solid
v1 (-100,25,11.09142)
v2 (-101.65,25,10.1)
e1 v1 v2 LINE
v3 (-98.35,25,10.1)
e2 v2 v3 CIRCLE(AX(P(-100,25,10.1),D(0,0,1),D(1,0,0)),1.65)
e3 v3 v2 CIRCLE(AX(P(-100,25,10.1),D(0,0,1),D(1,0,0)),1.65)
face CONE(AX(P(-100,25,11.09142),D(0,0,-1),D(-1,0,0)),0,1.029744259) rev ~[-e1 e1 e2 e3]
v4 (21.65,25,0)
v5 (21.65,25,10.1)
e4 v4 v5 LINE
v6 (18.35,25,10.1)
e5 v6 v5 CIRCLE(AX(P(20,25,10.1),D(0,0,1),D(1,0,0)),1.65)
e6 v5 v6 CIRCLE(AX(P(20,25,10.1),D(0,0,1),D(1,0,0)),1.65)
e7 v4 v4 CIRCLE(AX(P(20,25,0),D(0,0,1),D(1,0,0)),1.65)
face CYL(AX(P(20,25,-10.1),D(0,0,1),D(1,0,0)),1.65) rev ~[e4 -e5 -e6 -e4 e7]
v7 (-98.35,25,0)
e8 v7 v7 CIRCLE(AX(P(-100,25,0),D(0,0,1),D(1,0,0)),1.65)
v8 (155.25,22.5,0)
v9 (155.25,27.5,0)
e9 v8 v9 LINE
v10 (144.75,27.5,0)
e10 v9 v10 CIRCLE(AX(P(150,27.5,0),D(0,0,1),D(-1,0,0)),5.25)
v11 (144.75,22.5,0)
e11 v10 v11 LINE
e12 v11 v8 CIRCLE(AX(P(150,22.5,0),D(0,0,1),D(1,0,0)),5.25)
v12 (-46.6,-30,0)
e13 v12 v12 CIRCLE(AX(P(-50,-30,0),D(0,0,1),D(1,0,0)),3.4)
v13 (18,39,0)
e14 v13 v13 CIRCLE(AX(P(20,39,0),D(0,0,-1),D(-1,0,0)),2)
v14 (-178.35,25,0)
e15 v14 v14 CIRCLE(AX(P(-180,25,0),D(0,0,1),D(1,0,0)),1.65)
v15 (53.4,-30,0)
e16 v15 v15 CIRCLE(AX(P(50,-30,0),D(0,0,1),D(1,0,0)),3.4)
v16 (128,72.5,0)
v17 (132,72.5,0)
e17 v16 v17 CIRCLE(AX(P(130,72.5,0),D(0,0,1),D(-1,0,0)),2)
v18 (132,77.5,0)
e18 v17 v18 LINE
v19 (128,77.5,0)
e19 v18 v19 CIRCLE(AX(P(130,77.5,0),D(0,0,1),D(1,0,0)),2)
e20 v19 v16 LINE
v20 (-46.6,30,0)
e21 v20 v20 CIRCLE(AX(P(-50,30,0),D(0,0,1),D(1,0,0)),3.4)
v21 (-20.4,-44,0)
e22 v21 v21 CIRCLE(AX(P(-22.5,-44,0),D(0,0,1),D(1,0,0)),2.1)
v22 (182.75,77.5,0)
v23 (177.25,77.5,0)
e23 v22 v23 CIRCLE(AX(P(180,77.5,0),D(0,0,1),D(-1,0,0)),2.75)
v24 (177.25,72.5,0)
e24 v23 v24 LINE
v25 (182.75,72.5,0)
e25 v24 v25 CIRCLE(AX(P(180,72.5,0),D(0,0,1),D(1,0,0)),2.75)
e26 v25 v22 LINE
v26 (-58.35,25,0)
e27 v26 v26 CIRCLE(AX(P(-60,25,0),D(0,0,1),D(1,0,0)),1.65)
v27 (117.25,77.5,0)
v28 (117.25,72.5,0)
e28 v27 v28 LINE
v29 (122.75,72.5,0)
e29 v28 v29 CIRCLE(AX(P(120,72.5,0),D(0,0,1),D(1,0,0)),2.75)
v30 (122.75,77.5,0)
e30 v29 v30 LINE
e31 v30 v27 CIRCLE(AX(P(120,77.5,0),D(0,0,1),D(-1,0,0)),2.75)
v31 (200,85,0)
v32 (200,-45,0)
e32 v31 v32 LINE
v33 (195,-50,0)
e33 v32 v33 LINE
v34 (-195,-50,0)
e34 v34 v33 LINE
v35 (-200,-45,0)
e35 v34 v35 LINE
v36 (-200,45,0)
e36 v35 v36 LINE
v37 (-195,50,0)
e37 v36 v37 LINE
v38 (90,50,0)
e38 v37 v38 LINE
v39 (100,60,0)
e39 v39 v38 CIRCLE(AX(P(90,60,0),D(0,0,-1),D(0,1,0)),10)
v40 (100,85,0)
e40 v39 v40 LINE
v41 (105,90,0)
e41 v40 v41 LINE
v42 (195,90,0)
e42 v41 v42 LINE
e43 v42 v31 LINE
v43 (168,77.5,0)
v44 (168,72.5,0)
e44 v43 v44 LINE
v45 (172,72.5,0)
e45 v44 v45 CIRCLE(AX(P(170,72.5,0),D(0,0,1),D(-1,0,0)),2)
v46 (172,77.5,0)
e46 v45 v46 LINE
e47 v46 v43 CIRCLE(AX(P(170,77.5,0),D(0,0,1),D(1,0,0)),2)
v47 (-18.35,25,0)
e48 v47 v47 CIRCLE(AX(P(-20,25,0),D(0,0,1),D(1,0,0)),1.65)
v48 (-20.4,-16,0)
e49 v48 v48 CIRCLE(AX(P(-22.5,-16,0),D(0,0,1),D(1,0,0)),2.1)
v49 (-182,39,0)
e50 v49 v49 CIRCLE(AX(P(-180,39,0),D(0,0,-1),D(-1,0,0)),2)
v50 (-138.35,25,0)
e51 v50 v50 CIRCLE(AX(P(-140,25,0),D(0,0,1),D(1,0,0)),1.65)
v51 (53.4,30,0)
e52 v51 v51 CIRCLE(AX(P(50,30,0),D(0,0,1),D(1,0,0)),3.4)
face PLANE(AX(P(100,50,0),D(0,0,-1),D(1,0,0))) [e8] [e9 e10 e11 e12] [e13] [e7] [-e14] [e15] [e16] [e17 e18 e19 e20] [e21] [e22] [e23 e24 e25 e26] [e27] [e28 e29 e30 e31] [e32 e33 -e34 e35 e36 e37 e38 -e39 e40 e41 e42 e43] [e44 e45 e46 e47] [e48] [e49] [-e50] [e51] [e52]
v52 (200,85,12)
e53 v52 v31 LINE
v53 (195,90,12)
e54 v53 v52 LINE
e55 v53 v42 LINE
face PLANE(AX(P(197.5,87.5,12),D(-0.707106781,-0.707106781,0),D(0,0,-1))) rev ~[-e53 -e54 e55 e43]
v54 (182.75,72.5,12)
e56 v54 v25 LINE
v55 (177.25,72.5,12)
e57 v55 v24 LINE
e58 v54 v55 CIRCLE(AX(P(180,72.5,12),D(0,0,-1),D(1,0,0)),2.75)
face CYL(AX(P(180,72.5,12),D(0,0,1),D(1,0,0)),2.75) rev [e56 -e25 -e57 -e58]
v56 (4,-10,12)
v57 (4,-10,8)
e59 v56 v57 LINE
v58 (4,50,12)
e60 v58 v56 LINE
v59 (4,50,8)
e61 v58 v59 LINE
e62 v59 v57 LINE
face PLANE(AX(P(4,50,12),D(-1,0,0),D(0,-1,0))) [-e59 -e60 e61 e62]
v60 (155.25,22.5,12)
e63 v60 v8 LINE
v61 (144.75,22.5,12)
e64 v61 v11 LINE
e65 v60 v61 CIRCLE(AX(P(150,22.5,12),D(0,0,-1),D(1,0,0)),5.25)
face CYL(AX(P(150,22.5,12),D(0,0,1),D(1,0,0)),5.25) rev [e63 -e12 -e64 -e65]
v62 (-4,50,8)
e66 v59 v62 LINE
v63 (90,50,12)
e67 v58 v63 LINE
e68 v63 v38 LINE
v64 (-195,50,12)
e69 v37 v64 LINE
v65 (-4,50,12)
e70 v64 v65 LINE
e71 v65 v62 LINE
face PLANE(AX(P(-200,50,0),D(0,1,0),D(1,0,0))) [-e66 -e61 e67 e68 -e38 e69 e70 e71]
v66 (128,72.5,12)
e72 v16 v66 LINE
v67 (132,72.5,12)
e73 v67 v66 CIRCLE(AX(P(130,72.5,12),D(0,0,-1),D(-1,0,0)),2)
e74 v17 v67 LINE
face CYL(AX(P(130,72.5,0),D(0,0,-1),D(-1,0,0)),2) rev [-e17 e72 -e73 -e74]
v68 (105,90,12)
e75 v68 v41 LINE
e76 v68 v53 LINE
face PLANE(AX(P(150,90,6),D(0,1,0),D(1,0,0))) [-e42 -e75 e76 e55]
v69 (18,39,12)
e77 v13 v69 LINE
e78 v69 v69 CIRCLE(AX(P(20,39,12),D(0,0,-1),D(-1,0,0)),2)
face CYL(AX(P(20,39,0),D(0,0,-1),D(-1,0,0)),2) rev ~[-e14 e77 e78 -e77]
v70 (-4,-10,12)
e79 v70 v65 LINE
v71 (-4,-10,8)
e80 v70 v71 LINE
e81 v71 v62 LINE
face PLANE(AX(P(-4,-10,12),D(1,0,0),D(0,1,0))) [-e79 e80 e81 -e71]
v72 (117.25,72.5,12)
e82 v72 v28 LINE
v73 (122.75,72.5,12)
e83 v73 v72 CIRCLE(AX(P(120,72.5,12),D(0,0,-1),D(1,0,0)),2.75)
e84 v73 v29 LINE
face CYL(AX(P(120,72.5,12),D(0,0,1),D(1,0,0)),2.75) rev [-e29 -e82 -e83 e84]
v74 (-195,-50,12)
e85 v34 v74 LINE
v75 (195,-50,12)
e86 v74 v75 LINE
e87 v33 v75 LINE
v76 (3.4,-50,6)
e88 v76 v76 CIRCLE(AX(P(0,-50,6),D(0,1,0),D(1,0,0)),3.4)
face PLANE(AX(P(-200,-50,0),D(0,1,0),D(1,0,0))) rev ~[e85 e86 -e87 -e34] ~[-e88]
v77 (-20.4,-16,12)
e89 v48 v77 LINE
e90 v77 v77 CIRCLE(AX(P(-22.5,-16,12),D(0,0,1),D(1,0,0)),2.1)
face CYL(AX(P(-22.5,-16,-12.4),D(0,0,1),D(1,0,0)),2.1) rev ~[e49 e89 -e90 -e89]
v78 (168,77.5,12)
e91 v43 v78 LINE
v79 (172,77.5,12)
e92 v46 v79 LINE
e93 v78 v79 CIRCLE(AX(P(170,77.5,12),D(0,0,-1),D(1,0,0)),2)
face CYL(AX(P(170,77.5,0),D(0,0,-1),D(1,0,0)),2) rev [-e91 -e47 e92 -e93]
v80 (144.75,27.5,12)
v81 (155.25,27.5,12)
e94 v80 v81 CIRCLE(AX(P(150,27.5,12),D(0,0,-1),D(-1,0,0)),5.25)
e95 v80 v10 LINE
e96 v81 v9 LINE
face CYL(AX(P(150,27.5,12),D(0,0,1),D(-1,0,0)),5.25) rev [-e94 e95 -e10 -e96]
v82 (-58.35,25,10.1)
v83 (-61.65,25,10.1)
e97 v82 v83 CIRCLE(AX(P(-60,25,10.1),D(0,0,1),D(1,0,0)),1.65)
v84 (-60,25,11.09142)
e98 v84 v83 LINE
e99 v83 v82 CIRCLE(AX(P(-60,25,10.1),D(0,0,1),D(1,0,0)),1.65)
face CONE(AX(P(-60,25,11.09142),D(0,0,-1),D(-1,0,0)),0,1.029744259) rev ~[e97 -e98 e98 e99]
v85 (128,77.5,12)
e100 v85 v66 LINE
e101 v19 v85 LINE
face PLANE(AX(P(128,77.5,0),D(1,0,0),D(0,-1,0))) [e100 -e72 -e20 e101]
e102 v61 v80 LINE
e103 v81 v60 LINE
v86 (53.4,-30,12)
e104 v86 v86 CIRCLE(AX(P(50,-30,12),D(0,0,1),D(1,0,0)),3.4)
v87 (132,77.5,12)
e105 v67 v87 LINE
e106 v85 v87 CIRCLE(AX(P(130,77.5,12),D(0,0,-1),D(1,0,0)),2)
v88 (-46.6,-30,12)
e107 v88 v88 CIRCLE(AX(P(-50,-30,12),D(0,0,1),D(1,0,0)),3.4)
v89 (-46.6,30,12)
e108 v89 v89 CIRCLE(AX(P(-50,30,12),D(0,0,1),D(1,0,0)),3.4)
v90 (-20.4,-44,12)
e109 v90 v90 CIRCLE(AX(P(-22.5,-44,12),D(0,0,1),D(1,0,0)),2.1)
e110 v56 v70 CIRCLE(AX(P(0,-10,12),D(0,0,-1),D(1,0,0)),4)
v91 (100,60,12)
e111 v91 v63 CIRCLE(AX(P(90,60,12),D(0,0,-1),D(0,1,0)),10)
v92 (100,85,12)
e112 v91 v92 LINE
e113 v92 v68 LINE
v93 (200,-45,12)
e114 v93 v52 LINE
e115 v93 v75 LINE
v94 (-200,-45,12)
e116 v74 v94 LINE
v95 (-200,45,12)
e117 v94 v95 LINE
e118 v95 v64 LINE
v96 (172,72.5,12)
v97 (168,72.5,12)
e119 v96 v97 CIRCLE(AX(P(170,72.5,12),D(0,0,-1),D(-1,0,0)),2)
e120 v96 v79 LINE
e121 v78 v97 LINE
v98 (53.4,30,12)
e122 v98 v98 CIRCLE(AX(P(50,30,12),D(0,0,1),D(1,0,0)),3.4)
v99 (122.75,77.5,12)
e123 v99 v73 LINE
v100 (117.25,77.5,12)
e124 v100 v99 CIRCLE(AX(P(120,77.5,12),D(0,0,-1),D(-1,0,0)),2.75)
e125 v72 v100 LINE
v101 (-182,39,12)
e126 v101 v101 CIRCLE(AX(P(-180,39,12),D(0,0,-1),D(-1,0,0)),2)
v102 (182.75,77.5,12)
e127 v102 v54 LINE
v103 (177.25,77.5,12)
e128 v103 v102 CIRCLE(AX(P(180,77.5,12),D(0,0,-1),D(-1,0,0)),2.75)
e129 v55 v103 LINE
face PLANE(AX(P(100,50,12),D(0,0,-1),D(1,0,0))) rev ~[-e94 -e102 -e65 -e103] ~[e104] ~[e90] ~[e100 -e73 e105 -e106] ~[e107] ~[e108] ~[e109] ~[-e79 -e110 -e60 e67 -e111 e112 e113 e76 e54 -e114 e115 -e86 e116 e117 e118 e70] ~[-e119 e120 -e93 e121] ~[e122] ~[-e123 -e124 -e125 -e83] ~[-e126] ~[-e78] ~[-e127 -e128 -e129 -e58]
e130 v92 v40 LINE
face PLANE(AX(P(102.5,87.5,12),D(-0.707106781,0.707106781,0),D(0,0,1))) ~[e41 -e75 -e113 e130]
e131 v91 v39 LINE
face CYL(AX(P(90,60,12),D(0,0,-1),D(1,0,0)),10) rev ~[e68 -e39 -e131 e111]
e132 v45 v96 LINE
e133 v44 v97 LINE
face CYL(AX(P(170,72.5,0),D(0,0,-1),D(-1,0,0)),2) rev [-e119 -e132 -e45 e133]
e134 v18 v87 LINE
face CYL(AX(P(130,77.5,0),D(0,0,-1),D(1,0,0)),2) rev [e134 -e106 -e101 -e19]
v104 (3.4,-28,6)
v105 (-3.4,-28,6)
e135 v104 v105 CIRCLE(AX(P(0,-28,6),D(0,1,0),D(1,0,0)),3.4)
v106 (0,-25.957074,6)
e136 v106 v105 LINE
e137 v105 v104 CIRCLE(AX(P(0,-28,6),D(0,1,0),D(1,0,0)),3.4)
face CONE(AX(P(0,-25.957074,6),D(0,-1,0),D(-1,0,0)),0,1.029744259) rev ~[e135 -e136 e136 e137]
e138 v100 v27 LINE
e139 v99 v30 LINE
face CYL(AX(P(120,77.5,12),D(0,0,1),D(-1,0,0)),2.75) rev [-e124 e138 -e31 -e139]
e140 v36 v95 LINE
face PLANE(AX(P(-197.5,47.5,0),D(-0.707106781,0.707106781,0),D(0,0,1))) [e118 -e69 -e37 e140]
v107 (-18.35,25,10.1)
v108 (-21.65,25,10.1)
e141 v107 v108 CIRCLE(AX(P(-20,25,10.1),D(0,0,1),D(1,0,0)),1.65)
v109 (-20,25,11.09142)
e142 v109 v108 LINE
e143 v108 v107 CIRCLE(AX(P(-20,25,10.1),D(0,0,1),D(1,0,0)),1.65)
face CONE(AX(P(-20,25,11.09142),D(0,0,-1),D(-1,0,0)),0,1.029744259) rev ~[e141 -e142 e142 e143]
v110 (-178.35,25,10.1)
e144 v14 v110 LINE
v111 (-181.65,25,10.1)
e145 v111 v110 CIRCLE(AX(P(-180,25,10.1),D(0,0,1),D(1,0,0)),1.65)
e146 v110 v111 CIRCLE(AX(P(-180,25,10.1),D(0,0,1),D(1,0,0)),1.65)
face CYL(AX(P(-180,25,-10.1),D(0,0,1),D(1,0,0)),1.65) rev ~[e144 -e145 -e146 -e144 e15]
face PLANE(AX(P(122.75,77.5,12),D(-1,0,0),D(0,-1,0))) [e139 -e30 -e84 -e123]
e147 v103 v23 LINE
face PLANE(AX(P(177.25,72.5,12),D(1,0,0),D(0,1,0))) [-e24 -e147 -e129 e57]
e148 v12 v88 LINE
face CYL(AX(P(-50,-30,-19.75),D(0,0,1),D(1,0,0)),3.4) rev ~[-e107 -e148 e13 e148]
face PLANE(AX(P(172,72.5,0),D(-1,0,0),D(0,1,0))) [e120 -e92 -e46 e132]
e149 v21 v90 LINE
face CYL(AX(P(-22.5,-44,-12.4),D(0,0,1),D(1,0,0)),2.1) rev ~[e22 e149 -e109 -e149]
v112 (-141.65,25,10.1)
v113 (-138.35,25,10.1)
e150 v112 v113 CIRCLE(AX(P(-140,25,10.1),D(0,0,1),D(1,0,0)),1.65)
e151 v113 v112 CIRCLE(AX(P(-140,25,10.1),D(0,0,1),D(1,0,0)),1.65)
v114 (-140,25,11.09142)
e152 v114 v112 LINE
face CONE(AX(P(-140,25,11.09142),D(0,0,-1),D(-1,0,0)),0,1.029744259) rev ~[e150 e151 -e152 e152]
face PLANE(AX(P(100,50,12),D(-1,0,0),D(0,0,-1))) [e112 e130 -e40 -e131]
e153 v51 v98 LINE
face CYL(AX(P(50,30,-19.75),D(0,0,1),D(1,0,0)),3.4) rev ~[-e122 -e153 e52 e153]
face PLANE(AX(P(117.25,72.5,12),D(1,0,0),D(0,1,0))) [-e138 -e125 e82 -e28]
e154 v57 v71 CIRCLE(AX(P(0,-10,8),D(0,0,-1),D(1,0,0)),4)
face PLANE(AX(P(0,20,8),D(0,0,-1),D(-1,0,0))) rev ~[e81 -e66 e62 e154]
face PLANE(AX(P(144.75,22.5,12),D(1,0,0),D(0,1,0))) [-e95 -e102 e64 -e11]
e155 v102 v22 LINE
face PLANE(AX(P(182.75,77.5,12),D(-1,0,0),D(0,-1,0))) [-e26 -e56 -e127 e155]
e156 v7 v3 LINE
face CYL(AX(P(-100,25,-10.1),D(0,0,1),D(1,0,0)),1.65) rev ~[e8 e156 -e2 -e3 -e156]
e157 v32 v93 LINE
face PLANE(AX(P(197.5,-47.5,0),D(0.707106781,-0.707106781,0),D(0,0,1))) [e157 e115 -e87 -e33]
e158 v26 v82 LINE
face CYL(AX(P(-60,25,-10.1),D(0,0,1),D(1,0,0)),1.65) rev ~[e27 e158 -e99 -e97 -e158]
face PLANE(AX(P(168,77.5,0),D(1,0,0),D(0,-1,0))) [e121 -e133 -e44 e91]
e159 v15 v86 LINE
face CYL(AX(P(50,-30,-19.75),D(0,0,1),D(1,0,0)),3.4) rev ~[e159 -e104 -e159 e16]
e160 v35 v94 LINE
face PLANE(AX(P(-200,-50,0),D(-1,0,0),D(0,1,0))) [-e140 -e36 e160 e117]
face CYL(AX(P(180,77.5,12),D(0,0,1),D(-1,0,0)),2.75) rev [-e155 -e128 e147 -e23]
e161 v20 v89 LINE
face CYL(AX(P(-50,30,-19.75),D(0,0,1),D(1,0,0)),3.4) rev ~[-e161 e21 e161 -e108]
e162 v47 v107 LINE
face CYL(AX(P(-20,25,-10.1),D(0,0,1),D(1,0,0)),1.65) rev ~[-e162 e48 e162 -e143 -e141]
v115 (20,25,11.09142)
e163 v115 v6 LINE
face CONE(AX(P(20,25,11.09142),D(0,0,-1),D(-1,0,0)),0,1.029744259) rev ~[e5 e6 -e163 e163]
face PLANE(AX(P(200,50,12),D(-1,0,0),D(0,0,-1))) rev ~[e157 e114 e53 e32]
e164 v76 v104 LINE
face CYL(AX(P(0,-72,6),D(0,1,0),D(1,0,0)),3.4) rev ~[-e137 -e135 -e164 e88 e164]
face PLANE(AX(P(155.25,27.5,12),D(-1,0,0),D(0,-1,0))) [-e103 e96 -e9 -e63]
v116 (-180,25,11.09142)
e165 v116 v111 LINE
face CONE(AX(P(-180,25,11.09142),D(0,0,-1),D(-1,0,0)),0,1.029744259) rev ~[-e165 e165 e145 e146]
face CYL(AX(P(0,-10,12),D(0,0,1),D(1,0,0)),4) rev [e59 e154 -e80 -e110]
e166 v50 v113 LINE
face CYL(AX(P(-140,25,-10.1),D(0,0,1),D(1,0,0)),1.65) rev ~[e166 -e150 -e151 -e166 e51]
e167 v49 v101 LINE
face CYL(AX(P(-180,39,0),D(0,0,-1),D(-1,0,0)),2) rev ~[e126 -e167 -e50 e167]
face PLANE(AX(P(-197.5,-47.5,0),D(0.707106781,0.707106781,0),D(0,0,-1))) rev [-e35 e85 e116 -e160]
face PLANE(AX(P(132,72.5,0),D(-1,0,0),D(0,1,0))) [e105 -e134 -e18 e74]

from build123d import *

# Parameters (mm, degrees)
SKETCH1_W                      = 400
SKETCH1_H                      = 100
BOSS_EXTRUDE1_DEPTH            = 12
SKETCH2_W                      = 100
SKETCH2_H                      = 12
BOSS_EXTRUDE2_DEPTH            = 40
CUT_EXTRUDE1_DEPTH             = 4
M8_TAPPED_HOLE2_D              = 6.8
M8_TAPPED_HOLE2_DEPTH          = 22
M8_TAPPED_HOLE2_TIP            = 2.042926105
M5_TAPPED_HOLE1_D              = 4.2
M5_TAPPED_HOLE1_DEPTH          = 12.4
M5_TAPPED_HOLE1_TIP            = 1.2618073
M4_TAPPED_HOLE1_D              = 3.3
M4_TAPPED_HOLE1_DEPTH          = 10.1
M4_TAPPED_HOLE1_TIP            = 0.991420021
SKETCH10_R                     = 2
CUT_EXTRUDE2_DEPTH             = 220.645168397
M8_TAPPED_HOLE1_D              = 6.8
M8_TAPPED_HOLE1_DEPTH          = 19.75
M8_TAPPED_HOLE1_TIP            = 2.042926105
F_5_5_5_5_DIAMETER_HOLE1_D     = 5.5
F_5_5_5_5_DIAMETER_HOLE1_DEPTH = 76
F_5_5_5_5_DIAMETER_HOLE1_TIP   = 1.652366702
CUT_EXTRUDE3_DEPTH             = 220.645168397
CHAMFER1_SIZE                  = 5
FILLET1_R                      = 10
CUT_EXTRUDE4_DEPTH             = 220.645168397


with BuildPart() as part:
    # Sketch1 → Boss-Extrude1 (new body)
    with BuildSketch(Plane.XY):
        Rectangle(SKETCH1_W, SKETCH1_H)
    extrude(amount=BOSS_EXTRUDE1_DEPTH)

    # Sketch2 → Boss-Extrude2 (add)
    with BuildSketch(Plane(origin=(0, 50, 0), x_dir=(1, 0, 0), z_dir=(0, 1, 0))):
        with Locations((150, -6)):
            Rectangle(SKETCH2_W, SKETCH2_H)
    extrude(amount=BOSS_EXTRUDE2_DEPTH)

    # Sketch3 → Cut-Extrude1 (cut)
    with BuildSketch(Plane.XY.offset(12)):
        with BuildLine():
            Line((4, 50), (4, -10))
            ThreePointArc((4, -10), (0, -14), (-4, -10))
            Line((-4, -10), (-4, 50))
            ThreePointArc((-4, 50), (0, 54), (4, 50))
        make_face()
    extrude(amount=-CUT_EXTRUDE1_DEPTH, mode=Mode.SUBTRACT)

    # M8 Tapped Hole2
    with Locations(Plane(origin=(0, -50, 0), x_dir=(-1, 0, 0), z_dir=(0, -1, 0))):
        with Locations((0, -6)):
            Hole(M8_TAPPED_HOLE2_D / 2, depth=M8_TAPPED_HOLE2_DEPTH)
            with Locations((0, 0, -(M8_TAPPED_HOLE2_DEPTH + M8_TAPPED_HOLE2_TIP / 2))):  # 118° drill point
                Cone(0, M8_TAPPED_HOLE2_D / 2, M8_TAPPED_HOLE2_TIP, mode=Mode.SUBTRACT)

    # M5 Tapped Hole1
    with Locations(Plane(origin=(0, 0, 0), x_dir=(-1, 0, 0), z_dir=(0, 0, -1))):
        with Locations((22.5, -16), (22.5, -44)):
            Hole(M5_TAPPED_HOLE1_D / 2, depth=M5_TAPPED_HOLE1_DEPTH)
            with Locations((0, 0, -(M5_TAPPED_HOLE1_DEPTH + M5_TAPPED_HOLE1_TIP / 2))):  # 118° drill point
                Cone(0, M5_TAPPED_HOLE1_D / 2, M5_TAPPED_HOLE1_TIP, mode=Mode.SUBTRACT)

    # M4 Tapped Hole1
    with Locations(Plane(origin=(0, 0, 0), x_dir=(-1, 0, 0), z_dir=(0, 0, -1))):
        with Locations((180, 25), (140, 25), (100, 25), (60, 25), (20, 25), (-20, 25)):
            Hole(M4_TAPPED_HOLE1_D / 2, depth=M4_TAPPED_HOLE1_DEPTH)
            with Locations((0, 0, -(M4_TAPPED_HOLE1_DEPTH + M4_TAPPED_HOLE1_TIP / 2))):  # 118° drill point
                Cone(0, M4_TAPPED_HOLE1_D / 2, M4_TAPPED_HOLE1_TIP, mode=Mode.SUBTRACT)

    # Sketch10 → Cut-Extrude2 (cut, through all)
    with BuildSketch(Plane(origin=(0, 0, 0), x_dir=(-1, 0, 0), z_dir=(0, 0, -1))):
        with Locations((180, 39)):
            Circle(SKETCH10_R)
        with Locations((-20, 39)):
            Circle(SKETCH10_R)
    extrude(amount=-CUT_EXTRUDE2_DEPTH, mode=Mode.SUBTRACT)

    # M8 Tapped Hole1
    with Locations(Plane(origin=(0, 0, 0), x_dir=(-1, 0, 0), z_dir=(0, 0, -1))):
        with Locations((50, -30), (50, 30), (-50, -30), (-50, 30)):
            Hole(M8_TAPPED_HOLE1_D / 2, depth=M8_TAPPED_HOLE1_DEPTH)
            with Locations((0, 0, -(M8_TAPPED_HOLE1_DEPTH + M8_TAPPED_HOLE1_TIP / 2))):  # 118° drill point
                Cone(0, M8_TAPPED_HOLE1_D / 2, M8_TAPPED_HOLE1_TIP, mode=Mode.SUBTRACT)

    # Ø5.5 (5.5) Diameter Hole1
    with Locations(Plane.XY.offset(12)):
        with Locations((120, 75), (180, 75), (150, 25)):
            Hole(F_5_5_5_5_DIAMETER_HOLE1_D / 2, depth=F_5_5_5_5_DIAMETER_HOLE1_DEPTH)
            with Locations((0, 0, -(F_5_5_5_5_DIAMETER_HOLE1_DEPTH + F_5_5_5_5_DIAMETER_HOLE1_TIP / 2))):  # 118° drill point
                Cone(0, F_5_5_5_5_DIAMETER_HOLE1_D / 2, F_5_5_5_5_DIAMETER_HOLE1_TIP, mode=Mode.SUBTRACT)

    # Sketch15 → Cut-Extrude3 (cut, through all)
    with BuildSketch(Plane.XY.offset(12)):
        with BuildLine():
            Line((122.75, 77.5), (122.75, 72.5))
            ThreePointArc((122.75, 72.5), (120, 69.75), (117.25, 72.5))
            Line((117.25, 72.5), (117.25, 77.5))
            ThreePointArc((117.25, 77.5), (120, 80.25), (122.75, 77.5))
        make_face()
        with BuildLine():
            Line((182.75, 77.5), (182.75, 72.5))
            ThreePointArc((182.75, 72.5), (180, 69.75), (177.25, 72.5))
            Line((177.25, 72.5), (177.25, 77.5))
            ThreePointArc((177.25, 77.5), (180, 80.25), (182.75, 77.5))
        make_face()
        with BuildLine():
            Line((155.25, 27.5), (155.25, 22.5))
            ThreePointArc((155.25, 22.5), (150, 17.25), (144.75, 22.5))
            Line((144.75, 22.5), (144.75, 27.5))
            ThreePointArc((144.75, 27.5), (150, 32.75), (155.25, 27.5))
        make_face()
    extrude(amount=-CUT_EXTRUDE3_DEPTH, mode=Mode.SUBTRACT)

    # Chamfer1
    chamfer1_edges = [part.edges().sort_by_distance(p)[0] for p in [
        (100, 90, 6),
        (200, 90, 6),
        (200, -50, 6),
        (-200, 50, 6),
        (-200, -50, 6),
    ]]
    chamfer(chamfer1_edges, length=CHAMFER1_SIZE)

    # Fillet1
    fillet1_edges = [part.edges().sort_by_distance(p)[0] for p in [
        (100, 50, 6),
    ]]
    fillet(fillet1_edges, radius=FILLET1_R)

    # Sketch16 → Cut-Extrude4 (cut, through all)
    with BuildSketch(Plane(origin=(0, 0, 0), x_dir=(-1, 0, 0), z_dir=(0, 0, -1))):
        with BuildLine():
            Line((-132, 72.5), (-132, 77.5))
            ThreePointArc((-132, 77.5), (-130, 79.5), (-128, 77.5))
            Line((-128, 77.5), (-128, 72.5))
            ThreePointArc((-128, 72.5), (-130, 70.5), (-132, 72.5))
        make_face()
        with BuildLine():
            Line((-172, 72.5), (-172, 77.5))
            ThreePointArc((-172, 77.5), (-170, 79.5), (-168, 77.5))
            Line((-168, 77.5), (-168, 72.5))
            ThreePointArc((-168, 72.5), (-170, 70.5), (-172, 72.5))
        make_face()
    extrude(amount=-CUT_EXTRUDE4_DEPTH, mode=Mode.SUBTRACT)


solid = part.part
